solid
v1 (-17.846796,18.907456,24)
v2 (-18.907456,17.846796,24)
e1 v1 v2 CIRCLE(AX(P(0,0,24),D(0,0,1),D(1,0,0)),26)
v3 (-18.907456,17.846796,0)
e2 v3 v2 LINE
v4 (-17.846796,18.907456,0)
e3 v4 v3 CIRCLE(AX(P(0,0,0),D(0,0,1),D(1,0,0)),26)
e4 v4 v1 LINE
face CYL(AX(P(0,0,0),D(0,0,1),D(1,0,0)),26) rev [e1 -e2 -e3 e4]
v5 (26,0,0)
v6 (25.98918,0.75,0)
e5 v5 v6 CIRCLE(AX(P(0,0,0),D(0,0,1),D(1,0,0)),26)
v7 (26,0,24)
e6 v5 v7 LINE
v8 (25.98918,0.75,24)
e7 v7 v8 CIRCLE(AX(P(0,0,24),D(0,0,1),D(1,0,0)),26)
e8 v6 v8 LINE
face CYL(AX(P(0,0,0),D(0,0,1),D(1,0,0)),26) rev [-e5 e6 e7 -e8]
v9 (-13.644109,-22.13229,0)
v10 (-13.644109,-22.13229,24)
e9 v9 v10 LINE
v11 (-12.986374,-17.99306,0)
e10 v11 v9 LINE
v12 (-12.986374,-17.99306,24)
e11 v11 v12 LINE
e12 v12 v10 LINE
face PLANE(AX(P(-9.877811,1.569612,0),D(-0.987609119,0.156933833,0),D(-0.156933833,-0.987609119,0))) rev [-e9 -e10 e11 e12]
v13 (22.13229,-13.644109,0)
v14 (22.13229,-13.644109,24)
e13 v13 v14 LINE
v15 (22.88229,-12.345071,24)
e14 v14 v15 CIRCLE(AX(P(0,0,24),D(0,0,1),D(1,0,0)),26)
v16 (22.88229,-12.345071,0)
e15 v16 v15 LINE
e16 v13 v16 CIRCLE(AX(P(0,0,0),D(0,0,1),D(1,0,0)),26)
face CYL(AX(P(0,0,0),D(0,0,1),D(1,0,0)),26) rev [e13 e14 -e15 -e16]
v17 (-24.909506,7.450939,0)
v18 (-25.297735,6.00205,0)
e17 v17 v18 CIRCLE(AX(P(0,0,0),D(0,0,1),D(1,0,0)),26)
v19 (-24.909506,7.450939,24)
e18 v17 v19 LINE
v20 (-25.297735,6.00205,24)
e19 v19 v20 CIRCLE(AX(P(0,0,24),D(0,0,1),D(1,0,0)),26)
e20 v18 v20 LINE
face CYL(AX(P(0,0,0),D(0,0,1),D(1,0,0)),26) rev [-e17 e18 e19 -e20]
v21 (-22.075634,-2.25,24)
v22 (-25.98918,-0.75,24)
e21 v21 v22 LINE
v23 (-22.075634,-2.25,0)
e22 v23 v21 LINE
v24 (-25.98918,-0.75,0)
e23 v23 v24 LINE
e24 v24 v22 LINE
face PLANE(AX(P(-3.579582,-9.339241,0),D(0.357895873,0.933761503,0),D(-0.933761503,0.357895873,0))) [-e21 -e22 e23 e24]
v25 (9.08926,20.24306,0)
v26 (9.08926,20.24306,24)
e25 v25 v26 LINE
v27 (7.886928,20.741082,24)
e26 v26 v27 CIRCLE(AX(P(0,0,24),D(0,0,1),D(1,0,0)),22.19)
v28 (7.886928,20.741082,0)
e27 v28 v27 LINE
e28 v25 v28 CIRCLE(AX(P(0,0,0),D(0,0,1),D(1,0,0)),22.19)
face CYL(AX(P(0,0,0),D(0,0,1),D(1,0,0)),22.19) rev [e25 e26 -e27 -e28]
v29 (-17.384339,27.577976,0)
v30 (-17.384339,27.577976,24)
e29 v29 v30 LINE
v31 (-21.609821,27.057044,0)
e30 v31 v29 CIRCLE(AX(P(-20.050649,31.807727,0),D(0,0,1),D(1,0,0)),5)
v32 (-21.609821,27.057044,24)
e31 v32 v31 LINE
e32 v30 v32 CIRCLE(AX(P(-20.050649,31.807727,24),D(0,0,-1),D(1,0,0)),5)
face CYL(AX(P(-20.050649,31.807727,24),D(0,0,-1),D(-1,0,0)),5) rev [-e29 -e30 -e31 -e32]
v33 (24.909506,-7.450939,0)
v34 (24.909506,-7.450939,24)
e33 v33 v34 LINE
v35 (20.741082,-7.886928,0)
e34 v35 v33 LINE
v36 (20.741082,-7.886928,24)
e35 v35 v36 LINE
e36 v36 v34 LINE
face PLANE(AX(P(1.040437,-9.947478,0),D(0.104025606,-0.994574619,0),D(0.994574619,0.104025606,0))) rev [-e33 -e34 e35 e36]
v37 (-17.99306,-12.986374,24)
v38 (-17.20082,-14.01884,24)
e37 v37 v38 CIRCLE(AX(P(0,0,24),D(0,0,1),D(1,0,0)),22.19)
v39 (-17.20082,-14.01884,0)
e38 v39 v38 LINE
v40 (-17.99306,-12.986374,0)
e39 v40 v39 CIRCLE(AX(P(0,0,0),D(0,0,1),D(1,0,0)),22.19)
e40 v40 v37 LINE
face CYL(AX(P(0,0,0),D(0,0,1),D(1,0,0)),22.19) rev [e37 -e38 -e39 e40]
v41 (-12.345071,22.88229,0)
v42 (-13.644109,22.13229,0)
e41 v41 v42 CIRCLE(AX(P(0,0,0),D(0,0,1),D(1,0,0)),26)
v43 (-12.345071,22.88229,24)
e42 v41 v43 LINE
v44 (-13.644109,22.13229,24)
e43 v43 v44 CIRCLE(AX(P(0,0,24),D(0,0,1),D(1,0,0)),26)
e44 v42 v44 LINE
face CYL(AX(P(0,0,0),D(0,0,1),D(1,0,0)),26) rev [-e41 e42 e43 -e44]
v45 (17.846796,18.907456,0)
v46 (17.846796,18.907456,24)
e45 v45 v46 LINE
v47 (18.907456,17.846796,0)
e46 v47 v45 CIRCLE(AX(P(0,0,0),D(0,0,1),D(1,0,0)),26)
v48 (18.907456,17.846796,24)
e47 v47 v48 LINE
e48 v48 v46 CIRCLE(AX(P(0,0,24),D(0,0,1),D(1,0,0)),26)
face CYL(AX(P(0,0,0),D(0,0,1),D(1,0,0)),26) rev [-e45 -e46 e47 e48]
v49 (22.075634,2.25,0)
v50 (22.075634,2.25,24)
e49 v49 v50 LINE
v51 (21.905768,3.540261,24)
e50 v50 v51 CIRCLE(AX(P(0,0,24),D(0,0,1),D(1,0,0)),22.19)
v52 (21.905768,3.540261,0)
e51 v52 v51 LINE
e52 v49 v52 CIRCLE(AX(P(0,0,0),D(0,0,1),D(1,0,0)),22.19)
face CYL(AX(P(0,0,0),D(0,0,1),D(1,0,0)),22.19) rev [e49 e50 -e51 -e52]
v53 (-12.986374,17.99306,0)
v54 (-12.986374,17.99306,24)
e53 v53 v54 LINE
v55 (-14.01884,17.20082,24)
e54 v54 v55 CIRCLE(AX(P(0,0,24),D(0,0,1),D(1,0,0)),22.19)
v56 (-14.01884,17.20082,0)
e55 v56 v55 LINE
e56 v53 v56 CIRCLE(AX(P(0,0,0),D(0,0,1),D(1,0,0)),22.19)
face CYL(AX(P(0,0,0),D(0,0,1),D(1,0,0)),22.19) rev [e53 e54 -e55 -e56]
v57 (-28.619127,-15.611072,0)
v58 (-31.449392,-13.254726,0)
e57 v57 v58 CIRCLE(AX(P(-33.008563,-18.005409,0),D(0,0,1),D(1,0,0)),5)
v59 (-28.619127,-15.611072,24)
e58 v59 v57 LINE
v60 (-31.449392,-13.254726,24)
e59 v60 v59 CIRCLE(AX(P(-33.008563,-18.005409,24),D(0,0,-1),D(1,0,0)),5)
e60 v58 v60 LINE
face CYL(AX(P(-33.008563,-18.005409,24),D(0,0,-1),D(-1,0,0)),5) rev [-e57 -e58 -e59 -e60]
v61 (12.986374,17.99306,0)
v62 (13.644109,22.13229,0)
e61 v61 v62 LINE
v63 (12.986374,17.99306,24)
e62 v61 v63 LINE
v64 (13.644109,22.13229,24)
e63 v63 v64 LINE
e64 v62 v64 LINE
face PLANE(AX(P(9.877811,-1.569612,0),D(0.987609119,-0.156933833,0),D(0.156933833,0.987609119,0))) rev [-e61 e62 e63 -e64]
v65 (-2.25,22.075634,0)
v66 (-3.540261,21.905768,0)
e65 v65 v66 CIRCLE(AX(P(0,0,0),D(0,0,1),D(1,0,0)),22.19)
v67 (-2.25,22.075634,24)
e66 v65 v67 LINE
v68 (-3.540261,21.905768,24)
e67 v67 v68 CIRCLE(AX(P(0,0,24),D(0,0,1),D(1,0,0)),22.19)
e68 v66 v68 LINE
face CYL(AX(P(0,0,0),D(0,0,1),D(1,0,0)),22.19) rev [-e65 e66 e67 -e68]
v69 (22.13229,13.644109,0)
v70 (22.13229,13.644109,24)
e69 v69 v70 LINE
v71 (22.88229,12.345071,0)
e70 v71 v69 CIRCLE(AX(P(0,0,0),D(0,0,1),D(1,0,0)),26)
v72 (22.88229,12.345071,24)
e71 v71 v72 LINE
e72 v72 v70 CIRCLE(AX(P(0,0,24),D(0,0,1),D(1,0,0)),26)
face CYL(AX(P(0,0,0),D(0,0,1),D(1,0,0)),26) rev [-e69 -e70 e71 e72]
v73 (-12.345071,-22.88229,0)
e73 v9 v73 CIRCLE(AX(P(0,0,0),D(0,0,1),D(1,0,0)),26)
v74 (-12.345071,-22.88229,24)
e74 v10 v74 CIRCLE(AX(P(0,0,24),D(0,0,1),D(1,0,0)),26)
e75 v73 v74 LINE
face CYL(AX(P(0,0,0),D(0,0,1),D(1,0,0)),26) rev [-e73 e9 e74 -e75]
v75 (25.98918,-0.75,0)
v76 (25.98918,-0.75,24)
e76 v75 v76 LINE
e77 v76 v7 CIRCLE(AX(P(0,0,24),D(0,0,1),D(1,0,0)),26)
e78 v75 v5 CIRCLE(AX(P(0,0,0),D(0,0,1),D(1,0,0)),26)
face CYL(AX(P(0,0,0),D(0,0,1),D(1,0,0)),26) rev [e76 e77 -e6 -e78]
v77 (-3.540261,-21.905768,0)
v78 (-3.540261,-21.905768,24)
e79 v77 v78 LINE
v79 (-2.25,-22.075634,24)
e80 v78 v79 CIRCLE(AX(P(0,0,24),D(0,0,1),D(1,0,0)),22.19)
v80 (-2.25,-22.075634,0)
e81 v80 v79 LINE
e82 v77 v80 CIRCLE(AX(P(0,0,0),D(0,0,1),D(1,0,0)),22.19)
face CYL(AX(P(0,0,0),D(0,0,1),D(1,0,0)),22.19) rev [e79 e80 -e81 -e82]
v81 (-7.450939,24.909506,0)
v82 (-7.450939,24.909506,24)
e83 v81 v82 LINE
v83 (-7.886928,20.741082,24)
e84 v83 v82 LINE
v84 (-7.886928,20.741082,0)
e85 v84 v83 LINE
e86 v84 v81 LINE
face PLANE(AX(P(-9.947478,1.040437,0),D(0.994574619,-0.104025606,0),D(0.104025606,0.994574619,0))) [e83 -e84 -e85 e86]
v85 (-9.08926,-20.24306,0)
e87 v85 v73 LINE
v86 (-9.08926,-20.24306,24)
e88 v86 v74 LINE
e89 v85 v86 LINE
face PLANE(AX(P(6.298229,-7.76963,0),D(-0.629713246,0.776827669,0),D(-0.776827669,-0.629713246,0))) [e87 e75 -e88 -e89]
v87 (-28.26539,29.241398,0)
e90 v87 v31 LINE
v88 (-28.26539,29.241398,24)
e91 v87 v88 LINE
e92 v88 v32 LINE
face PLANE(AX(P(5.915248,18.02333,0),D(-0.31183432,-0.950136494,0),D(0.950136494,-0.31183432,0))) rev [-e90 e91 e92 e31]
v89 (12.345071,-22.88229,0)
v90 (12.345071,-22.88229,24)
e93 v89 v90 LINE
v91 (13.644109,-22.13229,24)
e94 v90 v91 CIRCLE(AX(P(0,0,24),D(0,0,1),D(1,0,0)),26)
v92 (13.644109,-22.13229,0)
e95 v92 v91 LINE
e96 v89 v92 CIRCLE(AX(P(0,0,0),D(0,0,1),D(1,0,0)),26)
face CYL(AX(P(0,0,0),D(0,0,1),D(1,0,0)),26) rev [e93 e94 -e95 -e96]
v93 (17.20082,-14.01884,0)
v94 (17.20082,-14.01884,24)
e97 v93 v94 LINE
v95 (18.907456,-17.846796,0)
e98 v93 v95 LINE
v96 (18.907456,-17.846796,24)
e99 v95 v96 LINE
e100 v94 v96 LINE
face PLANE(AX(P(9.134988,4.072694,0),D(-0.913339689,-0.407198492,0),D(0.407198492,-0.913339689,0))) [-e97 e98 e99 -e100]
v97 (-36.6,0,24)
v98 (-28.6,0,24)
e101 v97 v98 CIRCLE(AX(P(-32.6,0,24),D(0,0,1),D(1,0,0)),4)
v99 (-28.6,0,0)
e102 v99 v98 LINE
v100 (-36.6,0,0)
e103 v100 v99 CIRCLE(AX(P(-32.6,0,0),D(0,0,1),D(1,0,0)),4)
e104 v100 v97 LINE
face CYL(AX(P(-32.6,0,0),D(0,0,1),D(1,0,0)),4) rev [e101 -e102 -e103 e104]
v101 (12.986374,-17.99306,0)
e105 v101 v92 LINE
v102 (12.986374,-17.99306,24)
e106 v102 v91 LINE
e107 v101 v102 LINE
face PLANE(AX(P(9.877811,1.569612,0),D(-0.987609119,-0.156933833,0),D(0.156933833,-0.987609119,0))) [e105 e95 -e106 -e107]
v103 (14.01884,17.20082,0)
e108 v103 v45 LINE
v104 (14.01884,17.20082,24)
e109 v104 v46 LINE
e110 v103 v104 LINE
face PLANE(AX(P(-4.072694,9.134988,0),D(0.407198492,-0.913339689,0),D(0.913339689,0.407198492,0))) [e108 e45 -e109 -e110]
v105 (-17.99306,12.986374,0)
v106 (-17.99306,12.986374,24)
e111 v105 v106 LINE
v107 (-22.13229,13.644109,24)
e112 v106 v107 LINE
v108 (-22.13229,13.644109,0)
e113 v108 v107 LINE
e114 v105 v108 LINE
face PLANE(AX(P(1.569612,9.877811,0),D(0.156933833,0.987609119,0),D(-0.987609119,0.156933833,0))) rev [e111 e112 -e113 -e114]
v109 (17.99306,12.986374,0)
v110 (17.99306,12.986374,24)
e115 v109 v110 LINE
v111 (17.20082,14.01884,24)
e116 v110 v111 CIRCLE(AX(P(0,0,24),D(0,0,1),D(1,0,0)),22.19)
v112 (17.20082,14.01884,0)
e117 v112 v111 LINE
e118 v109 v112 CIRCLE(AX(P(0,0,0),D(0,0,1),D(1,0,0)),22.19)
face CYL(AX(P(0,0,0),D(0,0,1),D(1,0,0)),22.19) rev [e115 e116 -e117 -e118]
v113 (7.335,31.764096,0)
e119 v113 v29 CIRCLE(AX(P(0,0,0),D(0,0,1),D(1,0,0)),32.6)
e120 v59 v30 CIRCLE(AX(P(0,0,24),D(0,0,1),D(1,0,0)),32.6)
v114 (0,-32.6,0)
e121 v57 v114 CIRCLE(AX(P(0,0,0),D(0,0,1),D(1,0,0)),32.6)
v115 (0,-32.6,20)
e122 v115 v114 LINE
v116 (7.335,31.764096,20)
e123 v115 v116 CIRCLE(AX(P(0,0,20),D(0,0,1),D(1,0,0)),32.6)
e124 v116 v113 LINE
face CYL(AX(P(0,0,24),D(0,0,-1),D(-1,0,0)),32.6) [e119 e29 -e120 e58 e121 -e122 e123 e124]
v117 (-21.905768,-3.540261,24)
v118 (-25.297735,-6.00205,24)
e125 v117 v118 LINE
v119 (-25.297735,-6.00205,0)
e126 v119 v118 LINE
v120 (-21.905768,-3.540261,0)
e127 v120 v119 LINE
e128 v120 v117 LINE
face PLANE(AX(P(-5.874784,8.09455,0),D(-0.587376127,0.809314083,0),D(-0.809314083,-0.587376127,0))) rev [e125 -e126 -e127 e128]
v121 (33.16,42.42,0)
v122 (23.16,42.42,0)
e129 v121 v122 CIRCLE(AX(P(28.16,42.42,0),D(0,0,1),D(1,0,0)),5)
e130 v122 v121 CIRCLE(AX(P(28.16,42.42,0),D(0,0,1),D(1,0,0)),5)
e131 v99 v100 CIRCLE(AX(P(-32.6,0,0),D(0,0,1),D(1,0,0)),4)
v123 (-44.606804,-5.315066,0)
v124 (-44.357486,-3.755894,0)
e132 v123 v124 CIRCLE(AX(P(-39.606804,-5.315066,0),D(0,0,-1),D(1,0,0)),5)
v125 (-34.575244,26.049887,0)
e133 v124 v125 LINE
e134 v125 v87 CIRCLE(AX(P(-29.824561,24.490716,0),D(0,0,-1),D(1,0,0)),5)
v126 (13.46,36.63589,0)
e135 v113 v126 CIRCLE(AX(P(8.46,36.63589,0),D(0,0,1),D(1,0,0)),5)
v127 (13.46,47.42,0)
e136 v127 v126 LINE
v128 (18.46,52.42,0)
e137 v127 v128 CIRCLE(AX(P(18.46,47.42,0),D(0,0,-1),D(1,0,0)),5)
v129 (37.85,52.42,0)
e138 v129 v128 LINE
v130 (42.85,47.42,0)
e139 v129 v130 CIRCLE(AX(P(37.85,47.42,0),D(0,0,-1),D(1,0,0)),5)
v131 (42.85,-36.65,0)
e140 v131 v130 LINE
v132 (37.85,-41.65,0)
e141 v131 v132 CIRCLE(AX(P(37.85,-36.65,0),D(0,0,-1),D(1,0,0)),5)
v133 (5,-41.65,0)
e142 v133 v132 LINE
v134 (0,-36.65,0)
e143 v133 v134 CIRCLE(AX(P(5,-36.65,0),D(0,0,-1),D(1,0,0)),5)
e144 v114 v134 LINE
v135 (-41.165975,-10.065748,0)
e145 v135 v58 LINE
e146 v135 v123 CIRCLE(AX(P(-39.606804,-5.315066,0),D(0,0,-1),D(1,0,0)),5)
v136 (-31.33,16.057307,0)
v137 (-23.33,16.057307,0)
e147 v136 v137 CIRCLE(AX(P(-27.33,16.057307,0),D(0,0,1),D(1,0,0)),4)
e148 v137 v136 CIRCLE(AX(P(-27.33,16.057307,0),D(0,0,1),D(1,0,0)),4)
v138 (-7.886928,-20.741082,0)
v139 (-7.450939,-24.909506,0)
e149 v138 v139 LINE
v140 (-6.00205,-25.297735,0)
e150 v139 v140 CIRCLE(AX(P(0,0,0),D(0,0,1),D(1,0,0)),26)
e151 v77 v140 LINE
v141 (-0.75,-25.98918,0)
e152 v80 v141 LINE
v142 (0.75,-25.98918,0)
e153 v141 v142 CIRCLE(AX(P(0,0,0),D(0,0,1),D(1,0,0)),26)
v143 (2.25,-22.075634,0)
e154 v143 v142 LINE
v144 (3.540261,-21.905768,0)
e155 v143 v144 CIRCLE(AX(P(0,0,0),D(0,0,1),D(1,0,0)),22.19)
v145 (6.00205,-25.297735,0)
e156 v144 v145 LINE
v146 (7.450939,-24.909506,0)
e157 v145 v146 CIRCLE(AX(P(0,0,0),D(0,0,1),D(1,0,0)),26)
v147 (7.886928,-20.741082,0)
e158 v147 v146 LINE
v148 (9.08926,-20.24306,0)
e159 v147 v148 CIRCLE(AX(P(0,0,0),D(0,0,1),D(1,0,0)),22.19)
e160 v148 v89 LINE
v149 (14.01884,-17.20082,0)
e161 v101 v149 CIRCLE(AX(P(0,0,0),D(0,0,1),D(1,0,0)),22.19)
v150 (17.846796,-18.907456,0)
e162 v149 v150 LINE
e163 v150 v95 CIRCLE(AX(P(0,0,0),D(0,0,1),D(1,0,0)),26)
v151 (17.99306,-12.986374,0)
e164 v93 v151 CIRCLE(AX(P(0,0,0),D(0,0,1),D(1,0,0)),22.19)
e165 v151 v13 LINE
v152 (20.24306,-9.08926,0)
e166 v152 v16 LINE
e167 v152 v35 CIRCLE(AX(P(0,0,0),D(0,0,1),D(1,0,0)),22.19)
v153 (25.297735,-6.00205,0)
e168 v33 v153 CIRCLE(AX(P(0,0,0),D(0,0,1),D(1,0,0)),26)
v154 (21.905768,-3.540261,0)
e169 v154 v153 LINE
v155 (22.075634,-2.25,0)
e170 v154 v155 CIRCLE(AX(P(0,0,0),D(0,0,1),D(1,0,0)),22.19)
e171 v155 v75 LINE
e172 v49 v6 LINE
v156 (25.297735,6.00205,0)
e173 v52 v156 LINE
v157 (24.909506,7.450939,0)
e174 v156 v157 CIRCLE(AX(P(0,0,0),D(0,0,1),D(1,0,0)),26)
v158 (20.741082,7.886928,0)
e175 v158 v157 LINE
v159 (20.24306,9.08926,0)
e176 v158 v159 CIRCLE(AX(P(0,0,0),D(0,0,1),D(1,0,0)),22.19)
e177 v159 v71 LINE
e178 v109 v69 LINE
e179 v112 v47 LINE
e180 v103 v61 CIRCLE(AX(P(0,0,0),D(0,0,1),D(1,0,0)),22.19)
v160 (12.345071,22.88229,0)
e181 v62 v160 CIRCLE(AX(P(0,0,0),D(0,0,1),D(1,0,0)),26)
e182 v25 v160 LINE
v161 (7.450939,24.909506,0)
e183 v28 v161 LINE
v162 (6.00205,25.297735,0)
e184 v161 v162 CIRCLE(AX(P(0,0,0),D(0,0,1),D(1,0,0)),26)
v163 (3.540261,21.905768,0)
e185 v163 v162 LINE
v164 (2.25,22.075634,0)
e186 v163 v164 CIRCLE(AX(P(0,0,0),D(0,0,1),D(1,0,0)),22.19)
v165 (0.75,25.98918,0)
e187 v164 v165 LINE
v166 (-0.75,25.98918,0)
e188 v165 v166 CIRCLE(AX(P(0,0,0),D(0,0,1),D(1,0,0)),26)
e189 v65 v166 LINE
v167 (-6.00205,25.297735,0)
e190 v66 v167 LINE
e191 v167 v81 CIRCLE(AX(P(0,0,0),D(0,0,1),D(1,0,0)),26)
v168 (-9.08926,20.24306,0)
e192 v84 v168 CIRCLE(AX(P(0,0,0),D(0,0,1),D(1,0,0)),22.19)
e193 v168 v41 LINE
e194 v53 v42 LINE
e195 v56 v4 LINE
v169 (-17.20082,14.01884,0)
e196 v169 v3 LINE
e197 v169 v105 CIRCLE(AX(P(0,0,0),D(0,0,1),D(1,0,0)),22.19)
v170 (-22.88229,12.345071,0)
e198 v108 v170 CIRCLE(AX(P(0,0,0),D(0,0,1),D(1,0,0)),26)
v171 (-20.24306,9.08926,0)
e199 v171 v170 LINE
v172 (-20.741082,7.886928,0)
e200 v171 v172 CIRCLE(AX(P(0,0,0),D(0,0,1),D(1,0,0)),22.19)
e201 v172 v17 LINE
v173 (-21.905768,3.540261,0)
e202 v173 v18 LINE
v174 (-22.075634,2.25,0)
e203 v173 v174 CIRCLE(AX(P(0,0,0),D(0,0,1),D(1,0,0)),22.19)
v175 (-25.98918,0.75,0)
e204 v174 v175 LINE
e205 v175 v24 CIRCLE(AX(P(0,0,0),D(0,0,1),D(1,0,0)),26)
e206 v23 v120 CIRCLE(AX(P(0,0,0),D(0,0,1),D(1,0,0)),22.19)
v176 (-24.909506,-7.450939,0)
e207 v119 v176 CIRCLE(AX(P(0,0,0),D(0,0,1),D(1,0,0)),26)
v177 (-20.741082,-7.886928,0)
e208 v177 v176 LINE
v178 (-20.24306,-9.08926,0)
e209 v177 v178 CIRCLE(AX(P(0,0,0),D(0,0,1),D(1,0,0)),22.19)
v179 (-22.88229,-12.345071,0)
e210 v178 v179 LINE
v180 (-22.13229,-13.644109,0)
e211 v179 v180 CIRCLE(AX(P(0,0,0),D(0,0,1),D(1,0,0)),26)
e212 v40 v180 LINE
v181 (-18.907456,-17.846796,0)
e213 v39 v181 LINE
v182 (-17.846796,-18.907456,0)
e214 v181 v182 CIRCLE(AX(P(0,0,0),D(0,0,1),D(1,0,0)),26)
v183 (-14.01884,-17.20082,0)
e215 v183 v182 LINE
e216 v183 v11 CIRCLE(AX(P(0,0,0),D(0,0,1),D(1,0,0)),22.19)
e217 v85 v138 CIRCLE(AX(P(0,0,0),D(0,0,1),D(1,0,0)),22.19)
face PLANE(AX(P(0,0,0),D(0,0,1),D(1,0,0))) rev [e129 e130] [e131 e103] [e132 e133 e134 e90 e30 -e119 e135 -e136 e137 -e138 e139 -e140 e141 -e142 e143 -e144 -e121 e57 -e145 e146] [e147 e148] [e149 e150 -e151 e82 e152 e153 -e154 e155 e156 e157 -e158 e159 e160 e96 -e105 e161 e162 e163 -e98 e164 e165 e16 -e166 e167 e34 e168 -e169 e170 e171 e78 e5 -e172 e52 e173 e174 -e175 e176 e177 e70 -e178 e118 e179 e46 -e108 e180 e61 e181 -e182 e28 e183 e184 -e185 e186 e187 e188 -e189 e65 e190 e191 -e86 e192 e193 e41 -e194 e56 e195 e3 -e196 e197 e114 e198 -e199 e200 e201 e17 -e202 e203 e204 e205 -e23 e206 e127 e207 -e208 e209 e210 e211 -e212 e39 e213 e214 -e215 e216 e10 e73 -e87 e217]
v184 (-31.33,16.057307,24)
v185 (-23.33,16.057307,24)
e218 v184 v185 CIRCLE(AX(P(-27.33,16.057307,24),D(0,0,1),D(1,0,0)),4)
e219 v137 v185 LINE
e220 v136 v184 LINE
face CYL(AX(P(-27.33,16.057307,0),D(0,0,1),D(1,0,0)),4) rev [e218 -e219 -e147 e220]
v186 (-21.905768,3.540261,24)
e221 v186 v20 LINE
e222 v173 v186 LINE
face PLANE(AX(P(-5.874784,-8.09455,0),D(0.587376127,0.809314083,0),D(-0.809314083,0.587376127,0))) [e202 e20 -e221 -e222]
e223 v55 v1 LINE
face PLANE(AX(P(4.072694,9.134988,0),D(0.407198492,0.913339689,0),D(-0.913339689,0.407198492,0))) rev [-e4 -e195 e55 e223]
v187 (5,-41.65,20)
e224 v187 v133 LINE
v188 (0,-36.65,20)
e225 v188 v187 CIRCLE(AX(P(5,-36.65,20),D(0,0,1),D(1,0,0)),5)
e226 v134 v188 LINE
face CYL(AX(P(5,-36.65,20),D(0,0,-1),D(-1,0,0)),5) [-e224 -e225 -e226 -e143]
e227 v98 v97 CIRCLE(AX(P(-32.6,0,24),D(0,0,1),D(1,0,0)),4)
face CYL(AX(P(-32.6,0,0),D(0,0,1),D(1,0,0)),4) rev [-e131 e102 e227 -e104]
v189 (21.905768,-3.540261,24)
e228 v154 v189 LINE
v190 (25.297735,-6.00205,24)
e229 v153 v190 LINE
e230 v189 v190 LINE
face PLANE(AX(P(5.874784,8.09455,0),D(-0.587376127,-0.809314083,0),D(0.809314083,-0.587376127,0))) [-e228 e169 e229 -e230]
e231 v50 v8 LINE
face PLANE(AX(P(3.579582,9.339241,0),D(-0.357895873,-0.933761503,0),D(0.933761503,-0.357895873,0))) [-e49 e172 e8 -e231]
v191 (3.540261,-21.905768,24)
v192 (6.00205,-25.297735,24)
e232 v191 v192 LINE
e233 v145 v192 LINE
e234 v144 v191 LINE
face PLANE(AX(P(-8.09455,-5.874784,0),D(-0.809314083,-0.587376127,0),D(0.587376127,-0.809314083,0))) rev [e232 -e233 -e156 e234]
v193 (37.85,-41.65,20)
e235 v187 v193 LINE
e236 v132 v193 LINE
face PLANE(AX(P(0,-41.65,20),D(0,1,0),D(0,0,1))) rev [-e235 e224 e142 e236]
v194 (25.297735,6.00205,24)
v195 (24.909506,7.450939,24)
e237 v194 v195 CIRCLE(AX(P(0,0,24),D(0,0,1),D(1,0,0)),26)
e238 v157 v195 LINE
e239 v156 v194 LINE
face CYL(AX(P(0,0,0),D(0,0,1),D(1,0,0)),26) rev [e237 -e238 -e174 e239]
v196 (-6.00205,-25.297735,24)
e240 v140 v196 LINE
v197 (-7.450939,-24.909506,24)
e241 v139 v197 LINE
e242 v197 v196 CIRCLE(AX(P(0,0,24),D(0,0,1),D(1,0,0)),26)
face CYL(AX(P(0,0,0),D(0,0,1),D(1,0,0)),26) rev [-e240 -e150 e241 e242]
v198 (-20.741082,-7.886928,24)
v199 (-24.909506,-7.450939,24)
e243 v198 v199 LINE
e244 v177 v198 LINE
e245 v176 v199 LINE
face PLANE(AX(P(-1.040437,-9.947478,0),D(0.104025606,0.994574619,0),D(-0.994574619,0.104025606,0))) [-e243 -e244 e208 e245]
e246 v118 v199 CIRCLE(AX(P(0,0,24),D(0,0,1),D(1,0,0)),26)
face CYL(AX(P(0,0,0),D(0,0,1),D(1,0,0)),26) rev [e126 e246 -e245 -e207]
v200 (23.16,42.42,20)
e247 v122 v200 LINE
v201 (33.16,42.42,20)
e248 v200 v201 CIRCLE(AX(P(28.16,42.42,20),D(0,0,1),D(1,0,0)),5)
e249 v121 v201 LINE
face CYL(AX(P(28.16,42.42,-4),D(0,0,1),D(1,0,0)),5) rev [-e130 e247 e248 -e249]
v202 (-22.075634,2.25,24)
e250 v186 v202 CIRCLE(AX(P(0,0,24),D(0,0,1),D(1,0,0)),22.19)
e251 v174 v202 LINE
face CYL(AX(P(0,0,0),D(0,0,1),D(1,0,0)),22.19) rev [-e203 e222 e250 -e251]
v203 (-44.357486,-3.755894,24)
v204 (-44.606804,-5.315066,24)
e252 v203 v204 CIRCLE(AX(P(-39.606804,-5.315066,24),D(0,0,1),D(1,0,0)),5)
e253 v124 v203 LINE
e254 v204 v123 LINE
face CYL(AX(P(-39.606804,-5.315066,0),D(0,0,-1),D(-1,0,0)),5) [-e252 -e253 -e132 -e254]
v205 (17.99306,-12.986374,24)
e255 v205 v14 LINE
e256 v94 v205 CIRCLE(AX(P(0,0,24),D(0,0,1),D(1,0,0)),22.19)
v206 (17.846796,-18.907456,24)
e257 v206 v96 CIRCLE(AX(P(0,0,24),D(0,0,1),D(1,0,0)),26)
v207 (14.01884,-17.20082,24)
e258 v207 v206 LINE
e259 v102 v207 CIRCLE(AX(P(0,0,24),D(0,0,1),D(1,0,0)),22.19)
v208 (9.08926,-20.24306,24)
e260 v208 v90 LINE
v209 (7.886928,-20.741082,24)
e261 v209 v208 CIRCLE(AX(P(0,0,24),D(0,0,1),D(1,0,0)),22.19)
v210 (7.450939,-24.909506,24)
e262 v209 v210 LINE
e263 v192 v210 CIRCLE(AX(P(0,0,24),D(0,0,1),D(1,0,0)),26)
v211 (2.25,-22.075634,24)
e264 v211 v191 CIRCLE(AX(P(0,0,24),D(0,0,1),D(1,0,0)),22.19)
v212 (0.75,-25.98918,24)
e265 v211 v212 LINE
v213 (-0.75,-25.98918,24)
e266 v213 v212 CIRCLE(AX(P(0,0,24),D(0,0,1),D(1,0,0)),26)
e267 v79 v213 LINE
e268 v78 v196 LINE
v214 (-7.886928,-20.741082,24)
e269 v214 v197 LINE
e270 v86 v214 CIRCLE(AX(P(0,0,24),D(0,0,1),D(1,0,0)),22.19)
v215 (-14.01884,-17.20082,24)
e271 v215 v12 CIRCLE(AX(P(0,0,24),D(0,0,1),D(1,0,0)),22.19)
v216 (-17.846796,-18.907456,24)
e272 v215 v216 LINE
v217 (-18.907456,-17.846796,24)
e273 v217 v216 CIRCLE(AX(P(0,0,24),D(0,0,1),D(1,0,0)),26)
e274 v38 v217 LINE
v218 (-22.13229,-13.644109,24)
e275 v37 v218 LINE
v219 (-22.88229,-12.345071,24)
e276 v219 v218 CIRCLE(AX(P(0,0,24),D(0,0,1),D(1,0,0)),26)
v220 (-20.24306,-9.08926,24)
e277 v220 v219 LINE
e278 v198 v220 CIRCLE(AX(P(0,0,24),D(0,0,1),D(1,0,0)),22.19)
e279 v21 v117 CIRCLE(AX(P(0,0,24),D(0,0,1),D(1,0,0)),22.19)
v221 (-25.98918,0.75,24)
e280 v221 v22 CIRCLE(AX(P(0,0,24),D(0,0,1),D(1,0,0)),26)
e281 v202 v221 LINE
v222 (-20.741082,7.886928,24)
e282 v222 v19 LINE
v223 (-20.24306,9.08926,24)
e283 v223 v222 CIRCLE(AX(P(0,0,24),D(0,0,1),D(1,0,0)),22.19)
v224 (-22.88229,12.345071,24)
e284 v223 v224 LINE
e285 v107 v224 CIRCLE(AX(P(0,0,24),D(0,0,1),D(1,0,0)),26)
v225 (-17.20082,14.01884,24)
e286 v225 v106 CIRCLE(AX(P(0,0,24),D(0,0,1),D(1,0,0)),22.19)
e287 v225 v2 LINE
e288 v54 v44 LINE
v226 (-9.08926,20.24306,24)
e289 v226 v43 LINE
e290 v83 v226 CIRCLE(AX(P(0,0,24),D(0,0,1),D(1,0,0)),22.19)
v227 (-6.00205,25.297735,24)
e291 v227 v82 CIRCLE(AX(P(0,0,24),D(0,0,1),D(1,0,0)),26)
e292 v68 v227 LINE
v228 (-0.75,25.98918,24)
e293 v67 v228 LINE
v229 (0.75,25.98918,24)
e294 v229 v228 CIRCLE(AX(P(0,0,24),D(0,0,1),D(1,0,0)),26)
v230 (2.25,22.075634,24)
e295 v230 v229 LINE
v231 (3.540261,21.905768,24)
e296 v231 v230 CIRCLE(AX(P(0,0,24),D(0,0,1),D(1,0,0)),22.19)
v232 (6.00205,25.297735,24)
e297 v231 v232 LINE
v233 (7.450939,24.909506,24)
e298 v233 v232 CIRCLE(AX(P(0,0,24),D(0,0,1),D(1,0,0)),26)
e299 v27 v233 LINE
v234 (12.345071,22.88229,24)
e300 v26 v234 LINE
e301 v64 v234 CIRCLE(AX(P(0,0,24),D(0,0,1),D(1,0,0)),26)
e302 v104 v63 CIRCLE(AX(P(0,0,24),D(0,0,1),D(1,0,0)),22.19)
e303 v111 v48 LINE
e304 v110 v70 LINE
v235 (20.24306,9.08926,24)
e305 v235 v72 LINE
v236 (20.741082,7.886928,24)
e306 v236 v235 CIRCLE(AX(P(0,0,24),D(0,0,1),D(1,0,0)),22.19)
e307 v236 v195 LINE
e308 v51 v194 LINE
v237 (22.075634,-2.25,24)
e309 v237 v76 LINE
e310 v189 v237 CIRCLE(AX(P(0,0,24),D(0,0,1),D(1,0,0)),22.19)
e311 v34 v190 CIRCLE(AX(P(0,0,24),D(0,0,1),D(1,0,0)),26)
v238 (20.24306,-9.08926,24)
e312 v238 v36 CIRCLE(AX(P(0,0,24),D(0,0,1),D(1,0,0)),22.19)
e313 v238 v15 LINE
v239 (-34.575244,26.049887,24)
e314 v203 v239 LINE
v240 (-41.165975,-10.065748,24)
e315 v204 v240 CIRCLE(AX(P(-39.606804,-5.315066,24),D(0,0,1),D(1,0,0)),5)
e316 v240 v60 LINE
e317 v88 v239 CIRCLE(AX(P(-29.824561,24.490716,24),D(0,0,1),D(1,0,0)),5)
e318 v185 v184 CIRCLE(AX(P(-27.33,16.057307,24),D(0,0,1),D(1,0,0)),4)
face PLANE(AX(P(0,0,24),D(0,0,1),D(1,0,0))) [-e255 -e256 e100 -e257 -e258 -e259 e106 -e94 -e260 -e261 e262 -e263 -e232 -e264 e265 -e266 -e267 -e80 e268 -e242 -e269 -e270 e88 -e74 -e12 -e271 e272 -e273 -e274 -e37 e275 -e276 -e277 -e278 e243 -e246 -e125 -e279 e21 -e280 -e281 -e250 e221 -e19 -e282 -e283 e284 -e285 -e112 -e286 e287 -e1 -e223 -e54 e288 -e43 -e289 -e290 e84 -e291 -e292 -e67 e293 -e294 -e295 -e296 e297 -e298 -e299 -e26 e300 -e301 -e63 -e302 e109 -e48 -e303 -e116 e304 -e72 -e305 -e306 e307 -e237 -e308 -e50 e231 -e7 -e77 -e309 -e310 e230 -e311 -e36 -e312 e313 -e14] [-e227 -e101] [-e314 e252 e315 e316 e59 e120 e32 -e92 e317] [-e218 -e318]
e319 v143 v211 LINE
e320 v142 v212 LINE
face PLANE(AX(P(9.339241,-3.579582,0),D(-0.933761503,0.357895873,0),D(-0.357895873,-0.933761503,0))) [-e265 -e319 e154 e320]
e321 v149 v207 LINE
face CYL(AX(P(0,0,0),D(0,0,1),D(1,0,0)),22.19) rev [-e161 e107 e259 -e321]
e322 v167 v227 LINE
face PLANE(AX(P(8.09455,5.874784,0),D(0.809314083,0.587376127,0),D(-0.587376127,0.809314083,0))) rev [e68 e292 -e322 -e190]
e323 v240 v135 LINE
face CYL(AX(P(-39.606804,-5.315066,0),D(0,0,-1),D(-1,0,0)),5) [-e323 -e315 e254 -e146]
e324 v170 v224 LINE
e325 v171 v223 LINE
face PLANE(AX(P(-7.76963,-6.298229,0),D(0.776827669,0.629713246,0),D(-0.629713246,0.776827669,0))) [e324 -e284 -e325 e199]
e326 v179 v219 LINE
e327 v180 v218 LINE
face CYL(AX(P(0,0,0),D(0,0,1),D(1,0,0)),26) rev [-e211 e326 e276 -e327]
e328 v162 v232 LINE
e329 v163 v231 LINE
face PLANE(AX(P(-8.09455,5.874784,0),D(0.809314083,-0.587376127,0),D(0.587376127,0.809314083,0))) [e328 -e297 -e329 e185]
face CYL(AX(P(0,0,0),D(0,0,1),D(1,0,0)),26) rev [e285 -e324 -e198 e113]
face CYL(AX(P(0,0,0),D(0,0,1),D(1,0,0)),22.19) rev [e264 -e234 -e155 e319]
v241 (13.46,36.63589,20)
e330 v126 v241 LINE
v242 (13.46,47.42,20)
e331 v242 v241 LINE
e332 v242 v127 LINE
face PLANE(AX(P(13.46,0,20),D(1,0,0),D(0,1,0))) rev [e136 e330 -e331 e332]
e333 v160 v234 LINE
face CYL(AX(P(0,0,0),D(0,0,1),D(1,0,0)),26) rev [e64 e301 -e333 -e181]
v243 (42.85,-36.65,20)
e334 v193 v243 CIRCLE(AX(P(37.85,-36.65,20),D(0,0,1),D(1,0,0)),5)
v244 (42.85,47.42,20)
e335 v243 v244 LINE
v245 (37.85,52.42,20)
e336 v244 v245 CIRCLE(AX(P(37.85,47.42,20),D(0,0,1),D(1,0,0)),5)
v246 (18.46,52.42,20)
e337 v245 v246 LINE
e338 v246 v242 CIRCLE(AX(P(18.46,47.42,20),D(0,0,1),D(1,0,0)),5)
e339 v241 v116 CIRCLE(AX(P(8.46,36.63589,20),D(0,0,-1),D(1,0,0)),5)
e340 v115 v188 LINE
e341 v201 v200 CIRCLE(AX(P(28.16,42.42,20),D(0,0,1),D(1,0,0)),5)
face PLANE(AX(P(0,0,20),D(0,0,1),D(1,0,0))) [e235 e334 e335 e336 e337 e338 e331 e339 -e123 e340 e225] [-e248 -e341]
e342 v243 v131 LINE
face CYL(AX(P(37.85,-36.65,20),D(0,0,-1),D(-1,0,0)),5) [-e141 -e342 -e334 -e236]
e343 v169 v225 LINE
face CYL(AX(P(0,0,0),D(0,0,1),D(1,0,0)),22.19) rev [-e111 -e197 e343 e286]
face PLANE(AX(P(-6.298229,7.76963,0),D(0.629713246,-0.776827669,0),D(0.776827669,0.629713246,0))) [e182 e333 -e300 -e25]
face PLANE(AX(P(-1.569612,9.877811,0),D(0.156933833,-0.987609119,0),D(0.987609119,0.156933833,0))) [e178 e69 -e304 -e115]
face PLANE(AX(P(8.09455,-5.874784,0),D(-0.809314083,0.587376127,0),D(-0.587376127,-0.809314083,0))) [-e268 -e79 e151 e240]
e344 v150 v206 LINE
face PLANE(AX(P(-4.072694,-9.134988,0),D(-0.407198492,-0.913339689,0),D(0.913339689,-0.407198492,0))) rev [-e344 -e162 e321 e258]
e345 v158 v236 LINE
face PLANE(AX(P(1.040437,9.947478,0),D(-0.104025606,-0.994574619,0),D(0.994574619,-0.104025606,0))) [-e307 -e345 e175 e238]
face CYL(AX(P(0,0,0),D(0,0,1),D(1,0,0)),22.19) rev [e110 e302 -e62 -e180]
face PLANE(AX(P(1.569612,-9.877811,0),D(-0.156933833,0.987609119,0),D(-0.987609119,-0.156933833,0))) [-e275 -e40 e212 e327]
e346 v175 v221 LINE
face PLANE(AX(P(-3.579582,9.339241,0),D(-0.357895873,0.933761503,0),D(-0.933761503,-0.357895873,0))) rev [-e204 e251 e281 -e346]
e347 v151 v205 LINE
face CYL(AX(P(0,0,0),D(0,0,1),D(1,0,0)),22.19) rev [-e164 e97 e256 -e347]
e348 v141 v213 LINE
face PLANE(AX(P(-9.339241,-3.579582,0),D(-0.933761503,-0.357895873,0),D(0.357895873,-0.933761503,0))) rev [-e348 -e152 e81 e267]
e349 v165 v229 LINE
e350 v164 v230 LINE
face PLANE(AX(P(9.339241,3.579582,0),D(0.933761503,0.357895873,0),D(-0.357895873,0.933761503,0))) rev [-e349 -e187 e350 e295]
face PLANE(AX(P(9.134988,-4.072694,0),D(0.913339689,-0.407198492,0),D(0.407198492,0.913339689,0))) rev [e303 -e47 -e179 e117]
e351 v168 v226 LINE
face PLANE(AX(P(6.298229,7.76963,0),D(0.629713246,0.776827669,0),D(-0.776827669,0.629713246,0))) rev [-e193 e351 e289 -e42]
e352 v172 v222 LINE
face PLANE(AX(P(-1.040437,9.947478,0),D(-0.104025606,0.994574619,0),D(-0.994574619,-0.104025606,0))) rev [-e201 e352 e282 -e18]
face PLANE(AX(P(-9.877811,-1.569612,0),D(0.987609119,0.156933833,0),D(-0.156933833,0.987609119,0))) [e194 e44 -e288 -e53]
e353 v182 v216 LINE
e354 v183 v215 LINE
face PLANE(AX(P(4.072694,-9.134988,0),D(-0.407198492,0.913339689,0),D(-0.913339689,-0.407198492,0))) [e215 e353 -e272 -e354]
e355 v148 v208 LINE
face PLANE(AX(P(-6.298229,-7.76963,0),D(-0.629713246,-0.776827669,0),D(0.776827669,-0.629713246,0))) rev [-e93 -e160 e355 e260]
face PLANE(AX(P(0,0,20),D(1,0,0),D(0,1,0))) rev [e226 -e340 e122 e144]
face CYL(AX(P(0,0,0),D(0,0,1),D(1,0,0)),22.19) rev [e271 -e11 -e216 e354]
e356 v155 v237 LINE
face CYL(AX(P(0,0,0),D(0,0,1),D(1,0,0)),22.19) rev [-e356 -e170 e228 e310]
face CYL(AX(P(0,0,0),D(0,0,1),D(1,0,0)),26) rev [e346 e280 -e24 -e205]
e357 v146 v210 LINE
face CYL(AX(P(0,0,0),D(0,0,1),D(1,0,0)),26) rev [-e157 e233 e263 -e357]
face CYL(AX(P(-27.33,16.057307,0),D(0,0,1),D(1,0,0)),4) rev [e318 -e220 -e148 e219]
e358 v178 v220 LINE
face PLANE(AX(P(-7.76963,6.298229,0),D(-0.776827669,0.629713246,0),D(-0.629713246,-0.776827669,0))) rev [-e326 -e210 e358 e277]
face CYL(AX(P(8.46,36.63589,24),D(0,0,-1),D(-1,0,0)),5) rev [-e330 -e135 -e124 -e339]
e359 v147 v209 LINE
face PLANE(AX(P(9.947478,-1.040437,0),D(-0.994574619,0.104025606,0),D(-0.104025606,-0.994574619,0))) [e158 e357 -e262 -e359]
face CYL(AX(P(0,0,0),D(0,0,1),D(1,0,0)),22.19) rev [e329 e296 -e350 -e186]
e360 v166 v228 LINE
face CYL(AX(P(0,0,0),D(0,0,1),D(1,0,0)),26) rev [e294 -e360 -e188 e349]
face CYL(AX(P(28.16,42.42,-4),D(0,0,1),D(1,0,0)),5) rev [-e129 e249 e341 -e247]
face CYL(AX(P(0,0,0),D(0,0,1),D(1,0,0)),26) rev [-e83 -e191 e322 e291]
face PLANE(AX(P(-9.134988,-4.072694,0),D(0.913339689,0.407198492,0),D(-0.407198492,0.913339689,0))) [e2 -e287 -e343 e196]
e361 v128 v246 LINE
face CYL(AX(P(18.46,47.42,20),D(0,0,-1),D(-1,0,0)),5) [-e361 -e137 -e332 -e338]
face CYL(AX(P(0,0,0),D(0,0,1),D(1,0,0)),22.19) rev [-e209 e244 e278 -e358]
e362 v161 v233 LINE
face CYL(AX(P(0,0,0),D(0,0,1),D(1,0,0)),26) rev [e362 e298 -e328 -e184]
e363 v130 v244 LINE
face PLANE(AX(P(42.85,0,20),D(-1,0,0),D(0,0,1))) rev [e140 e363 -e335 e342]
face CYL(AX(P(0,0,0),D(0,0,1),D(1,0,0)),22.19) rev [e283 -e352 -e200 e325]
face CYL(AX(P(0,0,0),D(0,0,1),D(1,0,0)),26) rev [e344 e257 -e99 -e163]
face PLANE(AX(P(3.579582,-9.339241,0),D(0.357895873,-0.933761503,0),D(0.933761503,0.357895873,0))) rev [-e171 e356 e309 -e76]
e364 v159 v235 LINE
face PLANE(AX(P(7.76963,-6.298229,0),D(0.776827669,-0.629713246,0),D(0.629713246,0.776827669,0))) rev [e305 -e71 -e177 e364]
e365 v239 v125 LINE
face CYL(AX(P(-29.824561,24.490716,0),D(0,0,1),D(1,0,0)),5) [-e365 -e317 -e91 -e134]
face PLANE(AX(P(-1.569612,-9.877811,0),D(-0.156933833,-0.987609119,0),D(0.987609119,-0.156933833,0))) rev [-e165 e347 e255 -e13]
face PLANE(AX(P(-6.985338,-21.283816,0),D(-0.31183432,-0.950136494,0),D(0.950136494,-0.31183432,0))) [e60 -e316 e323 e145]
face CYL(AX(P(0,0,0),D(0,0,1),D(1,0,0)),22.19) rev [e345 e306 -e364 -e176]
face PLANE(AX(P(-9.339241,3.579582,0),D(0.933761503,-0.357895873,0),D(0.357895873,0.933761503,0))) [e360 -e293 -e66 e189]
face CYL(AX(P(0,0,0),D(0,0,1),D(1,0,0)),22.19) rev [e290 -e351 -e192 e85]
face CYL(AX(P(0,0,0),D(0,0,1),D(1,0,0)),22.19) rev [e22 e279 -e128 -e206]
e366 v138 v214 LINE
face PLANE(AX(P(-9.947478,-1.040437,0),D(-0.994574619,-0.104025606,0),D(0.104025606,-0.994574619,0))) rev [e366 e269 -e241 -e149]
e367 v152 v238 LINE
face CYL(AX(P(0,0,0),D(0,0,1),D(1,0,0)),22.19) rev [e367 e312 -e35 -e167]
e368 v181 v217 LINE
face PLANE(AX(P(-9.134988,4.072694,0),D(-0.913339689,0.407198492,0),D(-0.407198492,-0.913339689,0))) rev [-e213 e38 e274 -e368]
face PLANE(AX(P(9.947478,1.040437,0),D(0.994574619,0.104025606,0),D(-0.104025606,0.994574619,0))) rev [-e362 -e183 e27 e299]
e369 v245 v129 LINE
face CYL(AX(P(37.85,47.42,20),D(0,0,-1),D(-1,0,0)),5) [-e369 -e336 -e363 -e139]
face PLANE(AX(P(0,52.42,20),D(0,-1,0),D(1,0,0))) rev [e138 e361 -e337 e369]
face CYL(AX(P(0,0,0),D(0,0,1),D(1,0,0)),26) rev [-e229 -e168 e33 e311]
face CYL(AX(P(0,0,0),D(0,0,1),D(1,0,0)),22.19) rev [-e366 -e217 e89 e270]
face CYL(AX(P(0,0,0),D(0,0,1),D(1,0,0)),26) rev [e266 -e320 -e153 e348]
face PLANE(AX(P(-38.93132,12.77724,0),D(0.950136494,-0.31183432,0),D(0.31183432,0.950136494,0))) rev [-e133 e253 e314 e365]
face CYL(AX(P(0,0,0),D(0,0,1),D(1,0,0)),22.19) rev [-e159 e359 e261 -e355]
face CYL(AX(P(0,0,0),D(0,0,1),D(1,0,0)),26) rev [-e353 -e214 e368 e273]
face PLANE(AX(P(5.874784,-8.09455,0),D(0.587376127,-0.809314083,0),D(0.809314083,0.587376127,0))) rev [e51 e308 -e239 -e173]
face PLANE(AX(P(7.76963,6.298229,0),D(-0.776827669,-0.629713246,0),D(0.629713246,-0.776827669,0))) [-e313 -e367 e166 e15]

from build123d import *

# Parameters (mm, degrees)
MOUNTING_PLATE_DEPTH          = 20
SKETCH1_7_R                   = 32.6
SPLINE_HUB_BOSS_DEPTH         = 24
FLANGE_START                  = -24
FLANGE_BOSS_DEPTH             = 24
SKETCH3_4_R                   = 4
FLANGE_MOUNTING_HOLE_DEPTH    = 24
PLATE_HOLE_SKETCH_R           = 5
PLATE_MOUNTING_HOLE_DEPTH     = 24
INTERNAL_SPLINE_CUT_24T_DEPTH = 24
EDGE_FILLETS_R5_R             = 5


with BuildPart() as part:
    # Bracket Profile Sketch → Mounting Plate (new body)
    with BuildSketch(Plane.XY):
        with BuildLine():
            ThreePointArc((32.6, 0), (23.051681067, -23.051681067), (0, -32.6))
            Line((0, -32.6), (0, -41.65))
            Line((0, -41.65), (42.85, -41.65))
            Line((42.85, -41.65), (42.85, 52.42))
            Line((42.85, 52.42), (13.46, 52.42))
            Line((13.46, 52.42), (13.46, 29.691554355))
            ThreePointArc((13.46, 29.691554355), (27.400328465, 17.663012201), (32.6, 0))
        make_face()
    extrude(amount=MOUNTING_PLATE_DEPTH)

    # Sketch1_7 → Spline Hub Boss (add)
    with BuildSketch(Plane.XY):
        with Locations(Location((0, 0, 0), (0, 0, 270))):
            Circle(SKETCH1_7_R)
    extrude(amount=SPLINE_HUB_BOSS_DEPTH)

    # Flange and Hole Sketch → Flange Boss (add)
    with BuildSketch(Plane.XY.offset(24).offset(FLANGE_START)):
        with BuildLine():
            Line((-33.01607204, 30.800569947), (-45.916657839, -8.506576808))
            Line((-45.916657839, -8.506576808), (-29.489019594, -13.89811942))
            ThreePointArc((-29.489019594, -13.89811942), (-31.315952081, -9.059312625), (-32.354601227, -3.992465334))
            ThreePointArc((-32.354601227, -3.992465334), (-36.6, 0), (-32.354601227, 3.992465334))
            ThreePointArc((-32.354601227, 3.992465334), (-31.45055914, 8.580345552), (-29.899432156, 12.991687986))
            ThreePointArc((-29.899432156, 12.991687986), (-30.778793233, 18.08359035), (-25.90281989, 19.79403753))
            ThreePointArc((-25.90281989, 19.79403753), (-22.821560181, 23.279527292), (-19.275545993, 26.290936208))
            Line((-19.275545993, 26.290936208), (-33.01607204, 30.800569947))
        make_face()
    extrude(amount=FLANGE_BOSS_DEPTH)

    # Sketch3_4 → Flange Mounting Hole (cut)
    with BuildSketch(Plane.XY.offset(24).offset(FLANGE_START)):
        with Locations((-32.6, 0)):
            Circle(SKETCH3_4_R)
        with Locations((-27.33, 16.057306748)):
            Circle(SKETCH3_4_R)
    extrude(amount=FLANGE_MOUNTING_HOLE_DEPTH, mode=Mode.SUBTRACT)

    # Plate Hole Sketch → Plate Mounting Hole (cut)
    with BuildSketch(Plane.XY.offset(20)):
        with Locations((28.16, 42.42)):
            Circle(PLATE_HOLE_SKETCH_R)
    extrude(amount=-PLATE_MOUNTING_HOLE_DEPTH, mode=Mode.SUBTRACT)

    # Internal Spline Profile 24T → Internal Spline Cut 24T (cut)
    with BuildSketch(Plane.XY.offset(24)):
        with BuildLine():
            Line((-6.002050495, -25.297734876), (-3.540261306, -21.905767503))
            ThreePointArc((-3.540261306, -21.905767503), (-2.896376205, -22.000161474), (-2.25, -22.075633626))
            Line((-2.25, -22.075633626), (-0.75, -25.989180441))
            ThreePointArc((-0.75, -25.989180441), (0, -26), (0.75, -25.989180441))
            Line((0.75, -25.989180441), (2.25, -22.075633626))
            ThreePointArc((2.25, -22.075633626), (2.896376205, -22.000161474), (3.540261306, -21.905767503))
            Line((3.540261306, -21.905767503), (6.002050495, -25.297734876))
            ThreePointArc((6.002050495, -25.297734876), (6.729295173, -25.114071484), (7.450939234, -24.909506308))
            Line((7.450939234, -24.909506308), (7.886927524, -20.7410818))
            ThreePointArc((7.886927524, -20.7410818), (8.491745364, -20.500886826), (9.089259655, -20.243059525))
            Line((9.089259655, -20.243059525), (12.345071168, -22.882290486))
            ThreePointArc((12.345071168, -22.882290486), (13, -22.516660498), (13.644109273, -22.132290486))
            Line((13.644109273, -22.132290486), (12.986373972, -17.993059525))
            ThreePointArc((12.986373972, -17.993059525), (13.50841611, -17.604510621), (14.018839978, -17.200820494))
            Line((14.018839978, -17.200820494), (17.846795641, -18.907455813))
            ThreePointArc((17.846795641, -18.907455813), (18.384776311, -18.384776311), (18.907455813, -17.846795641))
            Line((18.907455813, -17.846795641), (17.200820494, -14.018839978))
            ThreePointArc((17.200820494, -14.018839978), (17.604510621, -13.50841611), (17.993059525, -12.986373972))
            Line((17.993059525, -12.986373972), (22.132290486, -13.644109273))
            ThreePointArc((22.132290486, -13.644109273), (22.516660498, -13), (22.882290486, -12.345071168))
            Line((22.882290486, -12.345071168), (20.243059525, -9.089259655))
            ThreePointArc((20.243059525, -9.089259655), (20.500886826, -8.491745364), (20.7410818, -7.886927524))
            Line((20.7410818, -7.886927524), (24.909506308, -7.450939234))
            ThreePointArc((24.909506308, -7.450939234), (25.114071484, -6.729295173), (25.297734876, -6.002050495))
            Line((25.297734876, -6.002050495), (21.905767503, -3.540261306))
            ThreePointArc((21.905767503, -3.540261306), (22.000161474, -2.896376205), (22.075633626, -2.25))
            Line((22.075633626, -2.25), (25.989180441, -0.75))
            ThreePointArc((25.989180441, -0.75), (25.99729497, -0.375039019), (26, 0))
            ThreePointArc((26, 0), (25.99729497, 0.375039019), (25.989180441, 0.75))
            Line((25.989180441, 0.75), (22.075633626, 2.25))
            ThreePointArc((22.075633626, 2.25), (22.000161474, 2.896376205), (21.905767503, 3.540261306))
            Line((21.905767503, 3.540261306), (25.297734876, 6.002050495))
            ThreePointArc((25.297734876, 6.002050495), (25.114071484, 6.729295173), (24.909506308, 7.450939234))
            Line((24.909506308, 7.450939234), (20.7410818, 7.886927524))
            ThreePointArc((20.7410818, 7.886927524), (20.500886826, 8.491745364), (20.243059525, 9.089259655))
            Line((20.243059525, 9.089259655), (22.882290486, 12.345071168))
            ThreePointArc((22.882290486, 12.345071168), (22.516660498, 13), (22.132290486, 13.644109273))
            Line((22.132290486, 13.644109273), (17.993059525, 12.986373972))
            ThreePointArc((17.993059525, 12.986373972), (17.604510621, 13.50841611), (17.200820494, 14.018839978))
            Line((17.200820494, 14.018839978), (18.907455813, 17.846795641))
            ThreePointArc((18.907455813, 17.846795641), (18.384776311, 18.384776311), (17.846795641, 18.907455813))
            Line((17.846795641, 18.907455813), (14.018839978, 17.200820494))
            ThreePointArc((14.018839978, 17.200820494), (13.50841611, 17.604510621), (12.986373972, 17.993059525))
            Line((12.986373972, 17.993059525), (13.644109273, 22.132290486))
            ThreePointArc((13.644109273, 22.132290486), (13, 22.516660498), (12.345071168, 22.882290486))
            Line((12.345071168, 22.882290486), (9.089259655, 20.243059525))
            ThreePointArc((9.089259655, 20.243059525), (8.491745364, 20.500886826), (7.886927524, 20.7410818))
            Line((7.886927524, 20.7410818), (7.450939234, 24.909506308))
            ThreePointArc((7.450939234, 24.909506308), (6.729295173, 25.114071484), (6.002050495, 25.297734876))
            Line((6.002050495, 25.297734876), (3.540261306, 21.905767503))
            ThreePointArc((3.540261306, 21.905767503), (2.896376205, 22.000161474), (2.25, 22.075633626))
            Line((2.25, 22.075633626), (0.75, 25.989180441))
            ThreePointArc((0.75, 25.989180441), (0, 26), (-0.75, 25.989180441))
            Line((-0.75, 25.989180441), (-2.25, 22.075633626))
            ThreePointArc((-2.25, 22.075633626), (-2.896376205, 22.000161474), (-3.540261306, 21.905767503))
            Line((-3.540261306, 21.905767503), (-6.002050495, 25.297734876))
            ThreePointArc((-6.002050495, 25.297734876), (-6.729295173, 25.114071484), (-7.450939234, 24.909506308))
            Line((-7.450939234, 24.909506308), (-7.886927524, 20.7410818))
            ThreePointArc((-7.886927524, 20.7410818), (-8.491745364, 20.500886826), (-9.089259655, 20.243059525))
            Line((-9.089259655, 20.243059525), (-12.345071168, 22.882290486))
            ThreePointArc((-12.345071168, 22.882290486), (-13, 22.516660498), (-13.644109273, 22.132290486))
            Line((-13.644109273, 22.132290486), (-12.986373972, 17.993059525))
            ThreePointArc((-12.986373972, 17.993059525), (-13.50841611, 17.604510621), (-14.018839978, 17.200820494))
            Line((-14.018839978, 17.200820494), (-17.846795641, 18.907455813))
            ThreePointArc((-17.846795641, 18.907455813), (-18.384776311, 18.384776311), (-18.907455813, 17.846795641))
            Line((-18.907455813, 17.846795641), (-17.200820494, 14.018839978))
            ThreePointArc((-17.200820494, 14.018839978), (-17.604510621, 13.50841611), (-17.993059525, 12.986373972))
            Line((-17.993059525, 12.986373972), (-22.132290486, 13.644109273))
            ThreePointArc((-22.132290486, 13.644109273), (-22.516660498, 13), (-22.882290486, 12.345071168))
            Line((-22.882290486, 12.345071168), (-20.243059525, 9.089259655))
            ThreePointArc((-20.243059525, 9.089259655), (-20.500886826, 8.491745364), (-20.7410818, 7.886927524))
            Line((-20.7410818, 7.886927524), (-24.909506308, 7.450939234))
            ThreePointArc((-24.909506308, 7.450939234), (-25.114071484, 6.729295173), (-25.297734876, 6.002050495))
            Line((-25.297734876, 6.002050495), (-21.905767503, 3.540261306))
            ThreePointArc((-21.905767503, 3.540261306), (-22.000161474, 2.896376205), (-22.075633626, 2.25))
            Line((-22.075633626, 2.25), (-25.989180441, 0.75))
            ThreePointArc((-25.989180441, 0.75), (-26, 0), (-25.989180441, -0.75))
            Line((-25.989180441, -0.75), (-22.075633626, -2.25))
            ThreePointArc((-22.075633626, -2.25), (-22.000161474, -2.896376205), (-21.905767503, -3.540261306))
            Line((-21.905767503, -3.540261306), (-25.297734876, -6.002050495))
            ThreePointArc((-25.297734876, -6.002050495), (-25.114071484, -6.729295173), (-24.909506308, -7.450939234))
            Line((-24.909506308, -7.450939234), (-20.7410818, -7.886927524))
            ThreePointArc((-20.7410818, -7.886927524), (-20.500886826, -8.491745364), (-20.243059525, -9.089259655))
            Line((-20.243059525, -9.089259655), (-22.882290486, -12.345071168))
            ThreePointArc((-22.882290486, -12.345071168), (-22.516660498, -13), (-22.132290486, -13.644109273))
            Line((-22.132290486, -13.644109273), (-17.993059525, -12.986373972))
            ThreePointArc((-17.993059525, -12.986373972), (-17.604510621, -13.50841611), (-17.200820494, -14.018839978))
            Line((-17.200820494, -14.018839978), (-18.907455813, -17.846795641))
            ThreePointArc((-18.907455813, -17.846795641), (-18.384776311, -18.384776311), (-17.846795641, -18.907455813))
            Line((-17.846795641, -18.907455813), (-14.018839978, -17.200820494))
            ThreePointArc((-14.018839978, -17.200820494), (-13.50841611, -17.604510621), (-12.986373972, -17.993059525))
            Line((-12.986373972, -17.993059525), (-13.644109273, -22.132290486))
            ThreePointArc((-13.644109273, -22.132290486), (-13, -22.516660498), (-12.345071168, -22.882290486))
            Line((-12.345071168, -22.882290486), (-9.089259655, -20.243059525))
            ThreePointArc((-9.089259655, -20.243059525), (-8.491745364, -20.500886826), (-7.886927524, -20.7410818))
            Line((-7.886927524, -20.7410818), (-7.450939234, -24.909506308))
            ThreePointArc((-7.450939234, -24.909506308), (-6.729295173, -25.114071484), (-6.002050495, -25.297734876))
        make_face()
    extrude(amount=-INTERNAL_SPLINE_CUT_24T_DEPTH, mode=Mode.SUBTRACT)

    # Edge Fillets R5
    edge_fillets_r5_edges = [part.edges().sort_by_distance(p)[0] for p in [
        (13.46, 29.691554355, 10),
        (13.46, 52.42, 10),
        (42.85, 52.42, 10),
        (42.85, -41.65, 10),
        (0, -41.65, 10),
        (-29.489019594, -13.89811942, 12),
        (-45.916657839, -8.506576808, 12),
        (-33.01607204, 30.800569947, 12),
        (-19.275545993, 26.290936208, 12),
    ]]
    fillet(edge_fillets_r5_edges, radius=EDGE_FILLETS_R5_R)


solid = part.part
